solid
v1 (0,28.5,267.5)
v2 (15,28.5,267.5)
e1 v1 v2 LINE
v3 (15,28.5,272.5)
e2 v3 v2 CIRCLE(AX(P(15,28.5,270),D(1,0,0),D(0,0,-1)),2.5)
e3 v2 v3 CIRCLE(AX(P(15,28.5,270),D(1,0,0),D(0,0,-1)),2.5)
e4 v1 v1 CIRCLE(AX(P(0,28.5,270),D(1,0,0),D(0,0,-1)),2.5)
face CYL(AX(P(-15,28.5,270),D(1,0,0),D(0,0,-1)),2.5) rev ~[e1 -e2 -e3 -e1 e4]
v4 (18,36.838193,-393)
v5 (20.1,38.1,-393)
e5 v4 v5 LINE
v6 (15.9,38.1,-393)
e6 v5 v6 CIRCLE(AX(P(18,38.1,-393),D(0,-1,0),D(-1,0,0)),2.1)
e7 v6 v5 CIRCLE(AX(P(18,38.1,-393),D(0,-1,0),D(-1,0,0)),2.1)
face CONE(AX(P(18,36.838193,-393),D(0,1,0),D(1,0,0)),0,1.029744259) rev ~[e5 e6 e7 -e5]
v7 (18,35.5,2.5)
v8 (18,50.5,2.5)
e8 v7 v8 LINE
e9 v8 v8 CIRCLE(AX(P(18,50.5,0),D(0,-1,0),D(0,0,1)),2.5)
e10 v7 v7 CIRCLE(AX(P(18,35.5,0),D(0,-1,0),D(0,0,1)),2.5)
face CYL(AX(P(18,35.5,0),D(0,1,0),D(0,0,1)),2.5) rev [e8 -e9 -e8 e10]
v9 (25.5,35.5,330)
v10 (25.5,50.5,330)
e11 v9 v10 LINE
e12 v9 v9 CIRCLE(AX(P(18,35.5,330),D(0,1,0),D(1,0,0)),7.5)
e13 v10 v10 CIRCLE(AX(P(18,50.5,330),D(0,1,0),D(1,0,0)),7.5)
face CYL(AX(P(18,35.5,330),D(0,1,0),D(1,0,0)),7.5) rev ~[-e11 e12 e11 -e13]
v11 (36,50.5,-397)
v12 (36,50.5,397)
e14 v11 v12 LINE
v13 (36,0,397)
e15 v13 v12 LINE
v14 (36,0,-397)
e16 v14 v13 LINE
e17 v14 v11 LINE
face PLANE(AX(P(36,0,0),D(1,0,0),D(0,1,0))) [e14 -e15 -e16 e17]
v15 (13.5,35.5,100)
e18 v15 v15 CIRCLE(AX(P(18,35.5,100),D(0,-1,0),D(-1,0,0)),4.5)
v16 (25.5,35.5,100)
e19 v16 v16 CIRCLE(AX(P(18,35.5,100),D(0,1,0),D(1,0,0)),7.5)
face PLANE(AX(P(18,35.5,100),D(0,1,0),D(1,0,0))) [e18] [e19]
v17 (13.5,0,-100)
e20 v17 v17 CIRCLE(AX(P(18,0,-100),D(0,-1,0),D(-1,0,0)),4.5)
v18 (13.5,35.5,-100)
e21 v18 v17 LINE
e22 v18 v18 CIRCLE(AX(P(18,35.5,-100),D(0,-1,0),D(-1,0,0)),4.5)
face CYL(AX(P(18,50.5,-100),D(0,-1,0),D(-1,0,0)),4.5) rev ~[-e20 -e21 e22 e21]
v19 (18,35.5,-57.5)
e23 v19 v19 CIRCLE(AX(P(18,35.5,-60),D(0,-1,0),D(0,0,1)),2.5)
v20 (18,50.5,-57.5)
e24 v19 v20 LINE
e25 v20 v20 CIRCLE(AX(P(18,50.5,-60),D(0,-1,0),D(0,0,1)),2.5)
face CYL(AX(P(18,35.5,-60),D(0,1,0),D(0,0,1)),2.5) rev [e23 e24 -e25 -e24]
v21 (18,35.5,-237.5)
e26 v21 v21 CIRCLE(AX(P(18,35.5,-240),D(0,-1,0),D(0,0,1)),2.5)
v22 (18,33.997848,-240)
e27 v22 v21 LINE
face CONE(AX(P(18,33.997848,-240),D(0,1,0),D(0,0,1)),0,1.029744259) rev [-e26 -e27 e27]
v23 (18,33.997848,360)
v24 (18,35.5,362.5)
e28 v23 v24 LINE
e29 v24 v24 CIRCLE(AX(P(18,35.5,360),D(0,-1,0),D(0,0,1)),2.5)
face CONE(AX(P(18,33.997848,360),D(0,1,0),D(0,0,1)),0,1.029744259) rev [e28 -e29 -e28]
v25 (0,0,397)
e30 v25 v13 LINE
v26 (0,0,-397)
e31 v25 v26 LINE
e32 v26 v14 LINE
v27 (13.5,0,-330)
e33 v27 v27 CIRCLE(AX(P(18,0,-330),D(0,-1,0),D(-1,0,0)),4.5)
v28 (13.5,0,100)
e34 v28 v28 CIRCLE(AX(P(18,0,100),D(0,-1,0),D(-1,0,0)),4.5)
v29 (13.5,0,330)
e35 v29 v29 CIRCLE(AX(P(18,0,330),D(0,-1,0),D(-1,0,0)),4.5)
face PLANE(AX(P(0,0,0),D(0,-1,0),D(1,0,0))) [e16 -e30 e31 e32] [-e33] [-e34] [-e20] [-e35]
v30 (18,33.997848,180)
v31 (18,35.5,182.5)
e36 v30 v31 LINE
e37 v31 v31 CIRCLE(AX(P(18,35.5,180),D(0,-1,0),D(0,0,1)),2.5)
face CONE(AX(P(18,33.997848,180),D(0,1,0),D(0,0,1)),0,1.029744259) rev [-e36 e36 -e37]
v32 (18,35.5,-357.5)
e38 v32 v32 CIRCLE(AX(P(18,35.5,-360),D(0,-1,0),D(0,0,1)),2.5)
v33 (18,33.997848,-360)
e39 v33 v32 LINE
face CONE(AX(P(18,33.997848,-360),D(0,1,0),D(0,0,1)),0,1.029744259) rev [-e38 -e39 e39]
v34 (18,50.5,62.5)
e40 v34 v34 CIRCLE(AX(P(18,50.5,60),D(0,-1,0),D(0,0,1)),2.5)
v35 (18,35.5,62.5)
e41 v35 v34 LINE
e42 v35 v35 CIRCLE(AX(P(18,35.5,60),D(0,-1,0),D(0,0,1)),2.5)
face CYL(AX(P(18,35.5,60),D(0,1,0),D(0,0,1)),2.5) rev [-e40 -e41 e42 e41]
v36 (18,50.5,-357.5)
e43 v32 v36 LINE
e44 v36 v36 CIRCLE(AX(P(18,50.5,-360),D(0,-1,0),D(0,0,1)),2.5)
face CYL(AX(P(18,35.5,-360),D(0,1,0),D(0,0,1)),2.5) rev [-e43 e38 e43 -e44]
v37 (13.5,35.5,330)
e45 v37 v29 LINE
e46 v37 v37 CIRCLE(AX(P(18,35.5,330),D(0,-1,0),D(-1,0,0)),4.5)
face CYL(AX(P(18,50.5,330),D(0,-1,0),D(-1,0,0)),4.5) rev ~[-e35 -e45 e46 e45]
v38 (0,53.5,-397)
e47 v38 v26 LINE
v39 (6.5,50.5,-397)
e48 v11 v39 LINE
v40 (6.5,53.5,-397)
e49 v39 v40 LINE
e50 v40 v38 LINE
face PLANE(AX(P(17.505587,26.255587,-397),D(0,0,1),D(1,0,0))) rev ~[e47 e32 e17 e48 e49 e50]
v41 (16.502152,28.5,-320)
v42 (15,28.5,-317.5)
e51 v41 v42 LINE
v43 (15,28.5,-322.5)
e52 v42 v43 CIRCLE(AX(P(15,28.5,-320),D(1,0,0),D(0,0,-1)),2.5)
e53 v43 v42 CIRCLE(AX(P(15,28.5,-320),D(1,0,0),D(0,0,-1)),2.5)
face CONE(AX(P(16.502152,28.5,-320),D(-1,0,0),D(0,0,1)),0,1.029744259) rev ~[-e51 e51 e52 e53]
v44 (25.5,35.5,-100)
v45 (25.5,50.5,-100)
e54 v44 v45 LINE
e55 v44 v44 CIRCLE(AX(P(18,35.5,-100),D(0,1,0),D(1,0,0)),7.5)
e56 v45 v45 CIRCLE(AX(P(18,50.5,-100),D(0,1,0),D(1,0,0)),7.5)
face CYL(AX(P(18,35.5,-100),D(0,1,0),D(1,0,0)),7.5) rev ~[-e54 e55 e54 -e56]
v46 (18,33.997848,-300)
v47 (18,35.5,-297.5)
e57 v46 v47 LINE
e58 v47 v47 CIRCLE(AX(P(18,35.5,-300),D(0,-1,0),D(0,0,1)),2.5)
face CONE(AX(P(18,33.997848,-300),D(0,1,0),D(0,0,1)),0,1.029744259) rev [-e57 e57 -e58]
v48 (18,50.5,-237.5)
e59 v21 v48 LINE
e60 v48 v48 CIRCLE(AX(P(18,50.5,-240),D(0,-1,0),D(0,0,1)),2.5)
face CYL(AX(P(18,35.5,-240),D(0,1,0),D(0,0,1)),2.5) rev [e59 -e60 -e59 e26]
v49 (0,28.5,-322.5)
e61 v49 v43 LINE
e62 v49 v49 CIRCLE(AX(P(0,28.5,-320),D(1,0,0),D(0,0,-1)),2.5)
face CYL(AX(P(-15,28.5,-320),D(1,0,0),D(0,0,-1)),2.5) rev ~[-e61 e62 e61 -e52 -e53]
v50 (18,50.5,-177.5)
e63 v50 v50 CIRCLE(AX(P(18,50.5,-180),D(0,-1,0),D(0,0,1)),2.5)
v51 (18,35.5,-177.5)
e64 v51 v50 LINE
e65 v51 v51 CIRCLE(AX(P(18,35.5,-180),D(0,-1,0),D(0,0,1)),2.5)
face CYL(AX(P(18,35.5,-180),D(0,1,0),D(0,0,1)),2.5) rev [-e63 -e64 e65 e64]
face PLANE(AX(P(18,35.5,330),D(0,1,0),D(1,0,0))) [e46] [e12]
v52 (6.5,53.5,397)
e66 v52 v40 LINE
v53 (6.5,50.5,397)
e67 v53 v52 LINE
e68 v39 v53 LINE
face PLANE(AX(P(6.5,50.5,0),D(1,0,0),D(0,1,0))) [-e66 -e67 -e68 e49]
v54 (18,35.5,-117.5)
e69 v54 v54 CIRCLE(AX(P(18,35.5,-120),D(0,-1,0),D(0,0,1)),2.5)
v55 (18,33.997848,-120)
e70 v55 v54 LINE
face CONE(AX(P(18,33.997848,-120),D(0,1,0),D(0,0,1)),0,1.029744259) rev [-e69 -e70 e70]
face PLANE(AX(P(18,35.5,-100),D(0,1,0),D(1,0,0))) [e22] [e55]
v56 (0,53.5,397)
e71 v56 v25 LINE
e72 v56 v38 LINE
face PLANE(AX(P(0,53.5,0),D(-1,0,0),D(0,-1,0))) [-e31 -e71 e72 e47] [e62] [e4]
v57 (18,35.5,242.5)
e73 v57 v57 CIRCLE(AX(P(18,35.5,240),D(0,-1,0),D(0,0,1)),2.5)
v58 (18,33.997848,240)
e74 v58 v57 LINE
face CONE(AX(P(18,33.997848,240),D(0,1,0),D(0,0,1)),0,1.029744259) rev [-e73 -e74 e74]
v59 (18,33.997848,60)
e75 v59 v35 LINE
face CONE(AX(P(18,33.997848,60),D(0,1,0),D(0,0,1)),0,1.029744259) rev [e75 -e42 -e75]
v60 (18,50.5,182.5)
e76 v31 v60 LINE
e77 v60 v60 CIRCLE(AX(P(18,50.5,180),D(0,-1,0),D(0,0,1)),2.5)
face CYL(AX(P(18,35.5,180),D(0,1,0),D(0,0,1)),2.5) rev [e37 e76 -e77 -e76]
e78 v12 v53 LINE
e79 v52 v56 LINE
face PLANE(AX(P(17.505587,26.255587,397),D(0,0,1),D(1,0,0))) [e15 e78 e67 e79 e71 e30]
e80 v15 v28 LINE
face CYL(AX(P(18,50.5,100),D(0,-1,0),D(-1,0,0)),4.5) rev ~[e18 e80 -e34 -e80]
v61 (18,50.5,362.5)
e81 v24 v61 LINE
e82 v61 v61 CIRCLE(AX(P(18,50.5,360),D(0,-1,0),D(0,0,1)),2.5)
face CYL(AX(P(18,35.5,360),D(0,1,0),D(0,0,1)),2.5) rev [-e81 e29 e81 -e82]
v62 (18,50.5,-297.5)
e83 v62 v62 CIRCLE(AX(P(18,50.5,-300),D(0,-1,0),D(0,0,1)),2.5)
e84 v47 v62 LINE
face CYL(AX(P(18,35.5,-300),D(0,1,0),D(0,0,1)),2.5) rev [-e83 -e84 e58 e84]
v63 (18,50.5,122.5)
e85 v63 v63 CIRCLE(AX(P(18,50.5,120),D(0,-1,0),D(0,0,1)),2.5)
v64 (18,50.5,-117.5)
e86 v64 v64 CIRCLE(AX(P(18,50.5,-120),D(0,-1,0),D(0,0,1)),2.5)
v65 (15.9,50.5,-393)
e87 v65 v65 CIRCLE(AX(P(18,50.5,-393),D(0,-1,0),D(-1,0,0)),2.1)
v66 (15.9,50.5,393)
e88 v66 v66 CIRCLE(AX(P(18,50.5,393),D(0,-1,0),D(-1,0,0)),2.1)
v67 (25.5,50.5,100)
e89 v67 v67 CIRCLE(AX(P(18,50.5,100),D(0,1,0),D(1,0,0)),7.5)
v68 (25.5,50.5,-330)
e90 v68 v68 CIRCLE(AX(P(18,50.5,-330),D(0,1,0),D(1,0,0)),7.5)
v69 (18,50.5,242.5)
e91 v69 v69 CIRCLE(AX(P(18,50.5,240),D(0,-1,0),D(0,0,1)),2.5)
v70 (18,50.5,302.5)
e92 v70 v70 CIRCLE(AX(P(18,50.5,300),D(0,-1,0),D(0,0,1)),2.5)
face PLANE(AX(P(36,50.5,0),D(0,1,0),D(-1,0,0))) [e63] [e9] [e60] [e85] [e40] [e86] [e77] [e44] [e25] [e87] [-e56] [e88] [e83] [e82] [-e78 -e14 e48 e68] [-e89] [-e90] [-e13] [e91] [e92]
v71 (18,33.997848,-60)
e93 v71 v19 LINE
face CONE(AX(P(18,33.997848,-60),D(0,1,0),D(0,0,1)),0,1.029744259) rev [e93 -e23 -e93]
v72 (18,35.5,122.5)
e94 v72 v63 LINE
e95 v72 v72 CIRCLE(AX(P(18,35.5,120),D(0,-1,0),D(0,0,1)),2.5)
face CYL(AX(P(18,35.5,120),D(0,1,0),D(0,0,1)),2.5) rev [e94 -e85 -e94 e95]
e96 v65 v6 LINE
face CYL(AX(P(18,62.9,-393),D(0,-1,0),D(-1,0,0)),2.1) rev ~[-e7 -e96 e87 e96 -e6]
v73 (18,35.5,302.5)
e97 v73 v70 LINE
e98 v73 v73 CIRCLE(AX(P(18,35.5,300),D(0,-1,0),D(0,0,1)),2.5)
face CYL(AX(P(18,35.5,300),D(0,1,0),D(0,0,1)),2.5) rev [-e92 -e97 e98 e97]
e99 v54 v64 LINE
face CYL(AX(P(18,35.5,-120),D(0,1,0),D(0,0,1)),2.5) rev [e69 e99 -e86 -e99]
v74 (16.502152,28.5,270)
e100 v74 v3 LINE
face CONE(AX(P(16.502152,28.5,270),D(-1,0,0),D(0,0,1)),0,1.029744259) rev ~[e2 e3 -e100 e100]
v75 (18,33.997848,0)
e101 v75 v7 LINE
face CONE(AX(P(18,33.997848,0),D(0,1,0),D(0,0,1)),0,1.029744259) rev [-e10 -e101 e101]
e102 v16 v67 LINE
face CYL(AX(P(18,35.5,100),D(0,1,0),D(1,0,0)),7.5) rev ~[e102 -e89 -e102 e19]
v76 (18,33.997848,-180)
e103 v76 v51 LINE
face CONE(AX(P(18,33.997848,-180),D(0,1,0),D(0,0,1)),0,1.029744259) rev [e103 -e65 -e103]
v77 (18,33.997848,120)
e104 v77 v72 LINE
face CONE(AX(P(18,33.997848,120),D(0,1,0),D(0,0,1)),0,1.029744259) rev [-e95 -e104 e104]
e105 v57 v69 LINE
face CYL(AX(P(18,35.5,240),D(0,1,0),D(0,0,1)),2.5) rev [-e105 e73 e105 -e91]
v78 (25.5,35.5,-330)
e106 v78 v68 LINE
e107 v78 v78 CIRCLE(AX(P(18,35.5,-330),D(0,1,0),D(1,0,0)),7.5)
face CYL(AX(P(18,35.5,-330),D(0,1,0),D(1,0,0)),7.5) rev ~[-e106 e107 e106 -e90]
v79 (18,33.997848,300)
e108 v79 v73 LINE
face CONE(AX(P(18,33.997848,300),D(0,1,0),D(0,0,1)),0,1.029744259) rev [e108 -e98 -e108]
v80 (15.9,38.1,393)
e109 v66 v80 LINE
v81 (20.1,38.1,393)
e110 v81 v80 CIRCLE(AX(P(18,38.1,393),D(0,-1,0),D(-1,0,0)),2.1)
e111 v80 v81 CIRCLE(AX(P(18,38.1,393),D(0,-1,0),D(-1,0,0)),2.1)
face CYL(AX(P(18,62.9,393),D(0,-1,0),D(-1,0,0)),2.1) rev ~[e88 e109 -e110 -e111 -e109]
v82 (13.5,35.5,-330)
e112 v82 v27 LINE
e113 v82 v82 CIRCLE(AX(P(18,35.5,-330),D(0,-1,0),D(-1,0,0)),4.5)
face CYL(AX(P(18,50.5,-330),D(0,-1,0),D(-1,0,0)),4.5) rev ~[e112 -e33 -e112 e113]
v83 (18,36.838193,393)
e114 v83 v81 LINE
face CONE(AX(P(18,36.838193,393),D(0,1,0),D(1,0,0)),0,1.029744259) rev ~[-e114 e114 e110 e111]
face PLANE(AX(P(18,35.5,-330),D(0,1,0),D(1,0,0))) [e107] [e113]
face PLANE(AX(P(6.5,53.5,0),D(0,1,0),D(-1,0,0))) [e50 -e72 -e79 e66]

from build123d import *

# Parameters (mm, degrees)
EXTRUDE_1_DEPTH           = 397
HOLE_WIZARD_M6_1_D        = 5
HOLE_WIZARD_M6_1_DEPTH    = 15
HOLE_WIZARD_M6_1_TIP      = 1.502151548
PATTERN_LINEAR_1_COUNT    = 13
PATTERN_LINEAR_1_PITCH    = 60
HOLE_WIZARD_1_D           = 9
HOLE_WIZARD_1_CBORE_D     = 15
HOLE_WIZARD_1_CBORE_DEPTH = 15
HOLE_WIZARD_M5_1_D        = 4.2
HOLE_WIZARD_M5_1_DEPTH    = 12.4
HOLE_WIZARD_M5_1_TIP      = 1.2618073


with BuildPart() as part:
    # 草图1 → 凸台-拉伸1 (new, symmetric)
    with BuildSketch(Plane.XY):
        Polygon((0, 0), (36, 0), (36, 50.5), (6.5, 50.5), (6.5, 53.5), (0, 53.5), align=None)
    extrude(amount=EXTRUDE_1_DEPTH, both=True)

    # M6 螺纹孔1
    with Locations(Plane.ZY):
        with Locations((-320, 28.5), (270, 28.5)):
            Hole(HOLE_WIZARD_M6_1_D / 2, depth=HOLE_WIZARD_M6_1_DEPTH)
            with Locations((0, 0, -(HOLE_WIZARD_M6_1_DEPTH + HOLE_WIZARD_M6_1_TIP / 2))):  # 118° drill point
                Cone(0, HOLE_WIZARD_M6_1_D / 2, HOLE_WIZARD_M6_1_TIP, mode=Mode.SUBTRACT)

    # 草图4 → M6 螺纹孔2 (revolve, cut)
    with BuildSketch(Plane(origin=(18, 50.5, -360), x_dir=(0, 0, 1), z_dir=(1, 0, 0))):
        Polygon((0, 0), (0, 16.502151548), (2.5, 15), (2.5, 0), align=None)
    hole_wizard_m6_2 = revolve(axis=Axis((18, 56.85, -360), (0, -1, 0)), mode=Mode.SUBTRACT)

    # 阵列(线性)1: M6 螺纹孔2 ×13
    with Locations(*[(0, 0, i * PATTERN_LINEAR_1_PITCH) for i in range(1, PATTERN_LINEAR_1_COUNT)]):
        add(hole_wizard_m6_2, mode=Mode.SUBTRACT)

    # 打孔尺寸(%根据)内六角圆柱头螺钉的类型1 (through all)
    with Locations(Plane(origin=(0, 50.5, 0), x_dir=(1, 0, 0), z_dir=(0, 1, 0))):
        with Locations((18, 330), (18, 100), (18, -100), (18, -330)):
            CounterBoreHole(HOLE_WIZARD_1_D / 2, HOLE_WIZARD_1_CBORE_D / 2, HOLE_WIZARD_1_CBORE_DEPTH)

    # M5 螺纹孔1
    with Locations(Plane(origin=(0, 50.5, 0), x_dir=(1, 0, 0), z_dir=(0, 1, 0))):
        with Locations((18, 393), (18, -393)):
            Hole(HOLE_WIZARD_M5_1_D / 2, depth=HOLE_WIZARD_M5_1_DEPTH)
            with Locations((0, 0, -(HOLE_WIZARD_M5_1_DEPTH + HOLE_WIZARD_M5_1_TIP / 2))):  # 118° drill point
                Cone(0, HOLE_WIZARD_M5_1_D / 2, HOLE_WIZARD_M5_1_TIP, mode=Mode.SUBTRACT)


solid = part.part
